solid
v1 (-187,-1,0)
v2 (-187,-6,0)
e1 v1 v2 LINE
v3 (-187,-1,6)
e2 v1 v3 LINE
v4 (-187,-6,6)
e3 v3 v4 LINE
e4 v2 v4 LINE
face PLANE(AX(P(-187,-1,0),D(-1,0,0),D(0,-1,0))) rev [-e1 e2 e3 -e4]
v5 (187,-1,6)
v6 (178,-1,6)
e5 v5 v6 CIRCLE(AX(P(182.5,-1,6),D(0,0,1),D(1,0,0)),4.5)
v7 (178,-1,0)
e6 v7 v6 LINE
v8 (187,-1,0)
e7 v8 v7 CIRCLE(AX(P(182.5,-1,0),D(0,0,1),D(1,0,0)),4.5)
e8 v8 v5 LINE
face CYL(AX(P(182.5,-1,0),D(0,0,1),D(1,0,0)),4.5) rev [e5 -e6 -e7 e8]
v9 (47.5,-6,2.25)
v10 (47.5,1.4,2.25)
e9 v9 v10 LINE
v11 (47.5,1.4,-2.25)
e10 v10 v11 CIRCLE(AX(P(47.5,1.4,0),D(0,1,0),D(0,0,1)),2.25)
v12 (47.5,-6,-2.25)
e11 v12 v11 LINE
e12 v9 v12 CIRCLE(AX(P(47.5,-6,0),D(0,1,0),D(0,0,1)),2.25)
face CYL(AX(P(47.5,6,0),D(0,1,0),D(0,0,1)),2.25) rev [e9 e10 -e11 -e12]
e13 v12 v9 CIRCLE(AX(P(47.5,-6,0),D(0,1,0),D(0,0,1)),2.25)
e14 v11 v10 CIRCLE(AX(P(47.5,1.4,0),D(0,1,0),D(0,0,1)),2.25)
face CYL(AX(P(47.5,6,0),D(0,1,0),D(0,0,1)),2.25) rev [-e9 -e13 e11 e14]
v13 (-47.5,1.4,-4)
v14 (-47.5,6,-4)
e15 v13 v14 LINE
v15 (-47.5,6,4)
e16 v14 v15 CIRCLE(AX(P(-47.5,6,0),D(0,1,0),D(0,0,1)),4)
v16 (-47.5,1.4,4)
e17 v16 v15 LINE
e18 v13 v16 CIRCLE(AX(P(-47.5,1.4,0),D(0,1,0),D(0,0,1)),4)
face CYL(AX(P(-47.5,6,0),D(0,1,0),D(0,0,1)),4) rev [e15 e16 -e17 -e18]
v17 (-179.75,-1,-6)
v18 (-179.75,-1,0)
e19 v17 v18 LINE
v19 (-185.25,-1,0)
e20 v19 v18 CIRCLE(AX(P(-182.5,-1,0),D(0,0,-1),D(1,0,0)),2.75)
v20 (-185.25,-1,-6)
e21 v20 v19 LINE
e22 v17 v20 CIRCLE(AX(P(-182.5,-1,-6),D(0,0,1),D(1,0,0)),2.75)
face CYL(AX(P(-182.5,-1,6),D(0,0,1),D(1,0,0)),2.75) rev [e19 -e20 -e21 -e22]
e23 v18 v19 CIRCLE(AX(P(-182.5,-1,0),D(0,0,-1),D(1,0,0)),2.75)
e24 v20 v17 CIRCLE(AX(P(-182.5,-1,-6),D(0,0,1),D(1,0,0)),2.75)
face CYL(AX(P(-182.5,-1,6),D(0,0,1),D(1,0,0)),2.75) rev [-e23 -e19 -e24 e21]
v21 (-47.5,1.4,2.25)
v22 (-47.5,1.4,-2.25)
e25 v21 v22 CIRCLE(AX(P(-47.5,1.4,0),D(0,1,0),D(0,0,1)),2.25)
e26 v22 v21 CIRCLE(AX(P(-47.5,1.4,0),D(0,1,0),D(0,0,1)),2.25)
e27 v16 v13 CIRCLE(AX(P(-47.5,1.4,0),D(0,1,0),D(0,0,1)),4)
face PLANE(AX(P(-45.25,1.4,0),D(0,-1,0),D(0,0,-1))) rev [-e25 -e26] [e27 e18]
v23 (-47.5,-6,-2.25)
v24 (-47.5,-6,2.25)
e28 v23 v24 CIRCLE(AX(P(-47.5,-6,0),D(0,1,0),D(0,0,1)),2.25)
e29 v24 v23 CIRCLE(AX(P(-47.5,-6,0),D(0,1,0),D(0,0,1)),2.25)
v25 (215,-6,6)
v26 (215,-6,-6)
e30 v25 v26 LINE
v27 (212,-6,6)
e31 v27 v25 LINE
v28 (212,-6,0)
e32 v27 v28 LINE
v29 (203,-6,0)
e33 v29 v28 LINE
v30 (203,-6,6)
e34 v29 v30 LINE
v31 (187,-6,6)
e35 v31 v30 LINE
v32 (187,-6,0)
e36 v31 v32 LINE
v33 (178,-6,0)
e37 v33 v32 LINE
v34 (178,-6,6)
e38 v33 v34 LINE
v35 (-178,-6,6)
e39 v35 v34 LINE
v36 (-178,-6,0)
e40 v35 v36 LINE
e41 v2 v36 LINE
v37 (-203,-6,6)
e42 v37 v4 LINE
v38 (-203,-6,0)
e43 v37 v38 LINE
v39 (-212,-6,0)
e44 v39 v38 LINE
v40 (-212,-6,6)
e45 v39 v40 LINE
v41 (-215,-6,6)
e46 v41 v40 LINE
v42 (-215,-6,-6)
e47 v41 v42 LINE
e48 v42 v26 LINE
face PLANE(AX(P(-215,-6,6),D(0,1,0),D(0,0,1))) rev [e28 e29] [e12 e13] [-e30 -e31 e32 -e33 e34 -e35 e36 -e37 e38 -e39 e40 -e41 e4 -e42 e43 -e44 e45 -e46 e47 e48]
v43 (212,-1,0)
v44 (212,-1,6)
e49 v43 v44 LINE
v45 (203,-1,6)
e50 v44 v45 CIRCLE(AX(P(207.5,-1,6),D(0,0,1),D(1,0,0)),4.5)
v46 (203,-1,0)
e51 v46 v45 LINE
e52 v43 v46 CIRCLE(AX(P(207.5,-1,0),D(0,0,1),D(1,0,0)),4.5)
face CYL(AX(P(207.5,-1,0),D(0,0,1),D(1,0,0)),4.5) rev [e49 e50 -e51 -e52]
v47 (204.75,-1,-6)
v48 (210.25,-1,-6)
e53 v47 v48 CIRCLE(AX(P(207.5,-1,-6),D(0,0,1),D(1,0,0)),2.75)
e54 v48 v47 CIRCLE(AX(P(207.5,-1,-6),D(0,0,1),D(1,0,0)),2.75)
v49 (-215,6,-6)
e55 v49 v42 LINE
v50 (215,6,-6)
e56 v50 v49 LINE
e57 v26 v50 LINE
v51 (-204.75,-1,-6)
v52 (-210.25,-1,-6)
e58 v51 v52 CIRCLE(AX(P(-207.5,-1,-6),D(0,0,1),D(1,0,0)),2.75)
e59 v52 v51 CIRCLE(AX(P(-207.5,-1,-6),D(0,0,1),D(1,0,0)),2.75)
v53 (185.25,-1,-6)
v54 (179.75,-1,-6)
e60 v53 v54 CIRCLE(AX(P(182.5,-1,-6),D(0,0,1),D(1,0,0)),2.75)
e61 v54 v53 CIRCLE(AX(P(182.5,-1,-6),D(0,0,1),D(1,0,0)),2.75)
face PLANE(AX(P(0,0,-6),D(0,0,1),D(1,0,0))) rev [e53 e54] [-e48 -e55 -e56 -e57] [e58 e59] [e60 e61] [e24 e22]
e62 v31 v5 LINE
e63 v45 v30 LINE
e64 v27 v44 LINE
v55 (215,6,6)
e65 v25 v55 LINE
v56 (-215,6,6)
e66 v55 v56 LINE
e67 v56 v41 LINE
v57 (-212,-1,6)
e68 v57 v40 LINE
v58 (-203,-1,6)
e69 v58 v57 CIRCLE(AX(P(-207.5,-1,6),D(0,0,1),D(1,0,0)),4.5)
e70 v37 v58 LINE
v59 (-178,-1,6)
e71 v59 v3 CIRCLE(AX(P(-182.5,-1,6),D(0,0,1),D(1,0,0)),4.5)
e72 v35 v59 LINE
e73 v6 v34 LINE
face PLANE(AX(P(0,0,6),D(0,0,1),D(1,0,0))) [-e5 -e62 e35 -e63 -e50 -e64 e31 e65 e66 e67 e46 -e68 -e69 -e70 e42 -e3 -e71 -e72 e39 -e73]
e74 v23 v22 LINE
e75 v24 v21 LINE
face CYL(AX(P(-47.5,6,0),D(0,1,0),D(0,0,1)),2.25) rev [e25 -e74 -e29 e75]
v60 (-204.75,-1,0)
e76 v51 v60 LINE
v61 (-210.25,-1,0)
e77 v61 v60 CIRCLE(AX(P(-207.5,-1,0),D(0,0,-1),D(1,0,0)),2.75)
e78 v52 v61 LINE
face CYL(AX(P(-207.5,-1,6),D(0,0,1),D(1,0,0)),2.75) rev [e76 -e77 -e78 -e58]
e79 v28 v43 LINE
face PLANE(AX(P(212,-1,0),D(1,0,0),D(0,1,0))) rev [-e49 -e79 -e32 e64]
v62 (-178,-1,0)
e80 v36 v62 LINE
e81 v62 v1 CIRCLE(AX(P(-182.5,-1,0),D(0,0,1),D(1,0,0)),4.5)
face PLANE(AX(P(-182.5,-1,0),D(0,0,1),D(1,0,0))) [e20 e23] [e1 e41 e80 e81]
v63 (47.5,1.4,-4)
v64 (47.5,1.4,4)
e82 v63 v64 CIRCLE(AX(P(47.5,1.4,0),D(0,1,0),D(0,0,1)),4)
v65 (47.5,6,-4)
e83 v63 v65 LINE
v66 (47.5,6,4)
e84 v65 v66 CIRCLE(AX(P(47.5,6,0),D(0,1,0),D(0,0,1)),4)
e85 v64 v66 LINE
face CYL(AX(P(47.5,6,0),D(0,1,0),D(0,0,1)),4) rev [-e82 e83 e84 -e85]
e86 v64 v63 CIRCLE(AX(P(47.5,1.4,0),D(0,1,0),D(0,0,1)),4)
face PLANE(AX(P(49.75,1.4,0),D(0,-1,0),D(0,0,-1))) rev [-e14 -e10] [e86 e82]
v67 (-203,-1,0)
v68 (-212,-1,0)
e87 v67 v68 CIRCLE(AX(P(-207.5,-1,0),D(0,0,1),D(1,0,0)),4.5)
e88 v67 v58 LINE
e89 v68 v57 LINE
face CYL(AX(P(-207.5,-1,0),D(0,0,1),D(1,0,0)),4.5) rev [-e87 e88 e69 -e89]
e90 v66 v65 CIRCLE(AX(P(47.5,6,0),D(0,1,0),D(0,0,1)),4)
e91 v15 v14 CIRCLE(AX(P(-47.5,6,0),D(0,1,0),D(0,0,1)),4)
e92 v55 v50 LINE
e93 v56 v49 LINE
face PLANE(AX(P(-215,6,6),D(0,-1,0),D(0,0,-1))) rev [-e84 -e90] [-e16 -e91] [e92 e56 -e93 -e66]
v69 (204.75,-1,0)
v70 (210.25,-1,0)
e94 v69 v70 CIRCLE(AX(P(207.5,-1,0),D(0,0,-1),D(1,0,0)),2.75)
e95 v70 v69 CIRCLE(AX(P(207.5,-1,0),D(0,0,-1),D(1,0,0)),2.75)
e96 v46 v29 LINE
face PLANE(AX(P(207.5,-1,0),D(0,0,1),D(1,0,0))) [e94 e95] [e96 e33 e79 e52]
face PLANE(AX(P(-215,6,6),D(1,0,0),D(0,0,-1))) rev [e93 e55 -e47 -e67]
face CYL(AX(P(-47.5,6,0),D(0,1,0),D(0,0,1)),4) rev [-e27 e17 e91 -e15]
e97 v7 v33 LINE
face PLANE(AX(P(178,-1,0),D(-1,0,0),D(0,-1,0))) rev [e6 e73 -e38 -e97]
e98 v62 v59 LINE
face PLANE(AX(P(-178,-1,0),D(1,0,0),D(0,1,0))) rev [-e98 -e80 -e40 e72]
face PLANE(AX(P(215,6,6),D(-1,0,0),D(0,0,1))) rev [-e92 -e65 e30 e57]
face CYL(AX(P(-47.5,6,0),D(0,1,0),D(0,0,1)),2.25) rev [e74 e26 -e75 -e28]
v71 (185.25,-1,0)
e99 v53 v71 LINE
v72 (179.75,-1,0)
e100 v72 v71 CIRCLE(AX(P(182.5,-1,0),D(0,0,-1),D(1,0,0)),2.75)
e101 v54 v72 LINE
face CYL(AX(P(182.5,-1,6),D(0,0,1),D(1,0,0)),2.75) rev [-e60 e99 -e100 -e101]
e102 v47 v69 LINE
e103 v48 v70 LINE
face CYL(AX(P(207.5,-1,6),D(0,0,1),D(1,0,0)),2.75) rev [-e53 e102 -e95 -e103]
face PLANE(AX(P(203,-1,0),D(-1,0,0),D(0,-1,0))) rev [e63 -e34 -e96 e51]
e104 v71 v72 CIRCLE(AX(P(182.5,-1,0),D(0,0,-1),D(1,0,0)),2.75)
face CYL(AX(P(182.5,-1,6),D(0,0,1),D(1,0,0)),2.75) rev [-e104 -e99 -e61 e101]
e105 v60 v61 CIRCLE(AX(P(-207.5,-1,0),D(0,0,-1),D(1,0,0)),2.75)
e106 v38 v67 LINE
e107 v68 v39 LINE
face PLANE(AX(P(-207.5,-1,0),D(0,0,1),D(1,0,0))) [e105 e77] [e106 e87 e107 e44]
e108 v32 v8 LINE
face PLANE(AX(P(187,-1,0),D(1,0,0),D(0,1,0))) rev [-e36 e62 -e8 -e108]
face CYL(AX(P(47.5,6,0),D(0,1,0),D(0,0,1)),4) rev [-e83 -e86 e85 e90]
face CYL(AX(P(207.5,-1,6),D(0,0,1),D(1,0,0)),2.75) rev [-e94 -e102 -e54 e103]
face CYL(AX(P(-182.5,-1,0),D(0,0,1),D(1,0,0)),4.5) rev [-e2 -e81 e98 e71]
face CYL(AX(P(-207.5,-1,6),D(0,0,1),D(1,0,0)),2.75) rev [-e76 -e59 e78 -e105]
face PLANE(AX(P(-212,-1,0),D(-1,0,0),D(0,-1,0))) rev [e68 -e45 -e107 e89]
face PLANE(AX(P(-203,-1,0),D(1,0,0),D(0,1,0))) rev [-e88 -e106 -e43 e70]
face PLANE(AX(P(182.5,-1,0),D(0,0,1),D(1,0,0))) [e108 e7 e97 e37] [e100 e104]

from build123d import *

# Parameters (mm, degrees)
SKETCH_1_W                = 430
SKETCH_1_H                = 12
EXTRUDE_1_DEPTH           = 6
HOLE_WIZARD_5_5_5_5_1_D   = 5.5
HOLE_WIZARD_2_D           = 4.5
HOLE_WIZARD_2_DEPTH       = 14
HOLE_WIZARD_2_CBORE_D     = 8
HOLE_WIZARD_2_CBORE_DEPTH = 4.6
HOLE_WIZARD_2_TIP         = 1.351936393
CUT_EXTRUDE_1_DEPTH       = 6


with BuildPart() as part:
    # 草图1 → 凸台-拉伸1 (new, symmetric)
    with BuildSketch(Plane.XY):
        Rectangle(SKETCH_1_W, SKETCH_1_H)
    extrude(amount=EXTRUDE_1_DEPTH, both=True)

    # Ø5.5 (5.5) 直径孔1 (through all)
    with Locations(Plane.XY.offset(6)):
        with Locations((-207.5, -1), (-182.5, -1), (182.5, -1), (207.5, -1)):
            Hole(HOLE_WIZARD_5_5_5_5_1_D / 2)

    # 打孔尺寸(%根据)内六角圆柱头螺钉的类型2
    with Locations(Plane(origin=(0, 6, 0), x_dir=(1, 0, 0), z_dir=(0, 1, 0))):
        with Locations((-47.5, 0), (47.5, 0)):
            CounterBoreHole(HOLE_WIZARD_2_D / 2, HOLE_WIZARD_2_CBORE_D / 2, HOLE_WIZARD_2_CBORE_DEPTH, depth=HOLE_WIZARD_2_DEPTH)
            with Locations((0, 0, -(HOLE_WIZARD_2_DEPTH + HOLE_WIZARD_2_TIP / 2))):  # 118° drill point
                Cone(0, HOLE_WIZARD_2_D / 2, HOLE_WIZARD_2_TIP, mode=Mode.SUBTRACT)

    # 草图9 → 切除-拉伸1 (cut)
    with BuildSketch(Plane.XY.offset(6)):
        with BuildLine():
            Line((-203, -1), (-203, -15.234595698))
            ThreePointArc((-203, -15.234595698), (-207.5, -19.734595698), (-212, -15.234595698))
            Line((-212, -15.234595698), (-212, -1))
            ThreePointArc((-212, -1), (-207.5, 3.5), (-203, -1))
        make_face()
        with BuildLine():
            Line((-178, -1), (-178, -15.234595698))
            ThreePointArc((-178, -15.234595698), (-182.5, -19.734595698), (-187, -15.234595698))
            Line((-187, -15.234595698), (-187, -1))
            ThreePointArc((-187, -1), (-182.5, 3.5), (-178, -1))
        make_face()
        with BuildLine():
            Line((187, -1), (187, -15.234595698))
            ThreePointArc((187, -15.234595698), (182.5, -19.734595698), (178, -15.234595698))
            Line((178, -15.234595698), (178, -1))
            ThreePointArc((178, -1), (182.5, 3.5), (187, -1))
        make_face()
        with BuildLine():
            Line((212, -1), (212, -15.234595698))
            ThreePointArc((212, -15.234595698), (207.5, -19.734595698), (203, -15.234595698))
            Line((203, -15.234595698), (203, -1))
            ThreePointArc((203, -1), (207.5, 3.5), (212, -1))
        make_face()
    extrude(amount=-CUT_EXTRUDE_1_DEPTH, mode=Mode.SUBTRACT)


solid = part.part
